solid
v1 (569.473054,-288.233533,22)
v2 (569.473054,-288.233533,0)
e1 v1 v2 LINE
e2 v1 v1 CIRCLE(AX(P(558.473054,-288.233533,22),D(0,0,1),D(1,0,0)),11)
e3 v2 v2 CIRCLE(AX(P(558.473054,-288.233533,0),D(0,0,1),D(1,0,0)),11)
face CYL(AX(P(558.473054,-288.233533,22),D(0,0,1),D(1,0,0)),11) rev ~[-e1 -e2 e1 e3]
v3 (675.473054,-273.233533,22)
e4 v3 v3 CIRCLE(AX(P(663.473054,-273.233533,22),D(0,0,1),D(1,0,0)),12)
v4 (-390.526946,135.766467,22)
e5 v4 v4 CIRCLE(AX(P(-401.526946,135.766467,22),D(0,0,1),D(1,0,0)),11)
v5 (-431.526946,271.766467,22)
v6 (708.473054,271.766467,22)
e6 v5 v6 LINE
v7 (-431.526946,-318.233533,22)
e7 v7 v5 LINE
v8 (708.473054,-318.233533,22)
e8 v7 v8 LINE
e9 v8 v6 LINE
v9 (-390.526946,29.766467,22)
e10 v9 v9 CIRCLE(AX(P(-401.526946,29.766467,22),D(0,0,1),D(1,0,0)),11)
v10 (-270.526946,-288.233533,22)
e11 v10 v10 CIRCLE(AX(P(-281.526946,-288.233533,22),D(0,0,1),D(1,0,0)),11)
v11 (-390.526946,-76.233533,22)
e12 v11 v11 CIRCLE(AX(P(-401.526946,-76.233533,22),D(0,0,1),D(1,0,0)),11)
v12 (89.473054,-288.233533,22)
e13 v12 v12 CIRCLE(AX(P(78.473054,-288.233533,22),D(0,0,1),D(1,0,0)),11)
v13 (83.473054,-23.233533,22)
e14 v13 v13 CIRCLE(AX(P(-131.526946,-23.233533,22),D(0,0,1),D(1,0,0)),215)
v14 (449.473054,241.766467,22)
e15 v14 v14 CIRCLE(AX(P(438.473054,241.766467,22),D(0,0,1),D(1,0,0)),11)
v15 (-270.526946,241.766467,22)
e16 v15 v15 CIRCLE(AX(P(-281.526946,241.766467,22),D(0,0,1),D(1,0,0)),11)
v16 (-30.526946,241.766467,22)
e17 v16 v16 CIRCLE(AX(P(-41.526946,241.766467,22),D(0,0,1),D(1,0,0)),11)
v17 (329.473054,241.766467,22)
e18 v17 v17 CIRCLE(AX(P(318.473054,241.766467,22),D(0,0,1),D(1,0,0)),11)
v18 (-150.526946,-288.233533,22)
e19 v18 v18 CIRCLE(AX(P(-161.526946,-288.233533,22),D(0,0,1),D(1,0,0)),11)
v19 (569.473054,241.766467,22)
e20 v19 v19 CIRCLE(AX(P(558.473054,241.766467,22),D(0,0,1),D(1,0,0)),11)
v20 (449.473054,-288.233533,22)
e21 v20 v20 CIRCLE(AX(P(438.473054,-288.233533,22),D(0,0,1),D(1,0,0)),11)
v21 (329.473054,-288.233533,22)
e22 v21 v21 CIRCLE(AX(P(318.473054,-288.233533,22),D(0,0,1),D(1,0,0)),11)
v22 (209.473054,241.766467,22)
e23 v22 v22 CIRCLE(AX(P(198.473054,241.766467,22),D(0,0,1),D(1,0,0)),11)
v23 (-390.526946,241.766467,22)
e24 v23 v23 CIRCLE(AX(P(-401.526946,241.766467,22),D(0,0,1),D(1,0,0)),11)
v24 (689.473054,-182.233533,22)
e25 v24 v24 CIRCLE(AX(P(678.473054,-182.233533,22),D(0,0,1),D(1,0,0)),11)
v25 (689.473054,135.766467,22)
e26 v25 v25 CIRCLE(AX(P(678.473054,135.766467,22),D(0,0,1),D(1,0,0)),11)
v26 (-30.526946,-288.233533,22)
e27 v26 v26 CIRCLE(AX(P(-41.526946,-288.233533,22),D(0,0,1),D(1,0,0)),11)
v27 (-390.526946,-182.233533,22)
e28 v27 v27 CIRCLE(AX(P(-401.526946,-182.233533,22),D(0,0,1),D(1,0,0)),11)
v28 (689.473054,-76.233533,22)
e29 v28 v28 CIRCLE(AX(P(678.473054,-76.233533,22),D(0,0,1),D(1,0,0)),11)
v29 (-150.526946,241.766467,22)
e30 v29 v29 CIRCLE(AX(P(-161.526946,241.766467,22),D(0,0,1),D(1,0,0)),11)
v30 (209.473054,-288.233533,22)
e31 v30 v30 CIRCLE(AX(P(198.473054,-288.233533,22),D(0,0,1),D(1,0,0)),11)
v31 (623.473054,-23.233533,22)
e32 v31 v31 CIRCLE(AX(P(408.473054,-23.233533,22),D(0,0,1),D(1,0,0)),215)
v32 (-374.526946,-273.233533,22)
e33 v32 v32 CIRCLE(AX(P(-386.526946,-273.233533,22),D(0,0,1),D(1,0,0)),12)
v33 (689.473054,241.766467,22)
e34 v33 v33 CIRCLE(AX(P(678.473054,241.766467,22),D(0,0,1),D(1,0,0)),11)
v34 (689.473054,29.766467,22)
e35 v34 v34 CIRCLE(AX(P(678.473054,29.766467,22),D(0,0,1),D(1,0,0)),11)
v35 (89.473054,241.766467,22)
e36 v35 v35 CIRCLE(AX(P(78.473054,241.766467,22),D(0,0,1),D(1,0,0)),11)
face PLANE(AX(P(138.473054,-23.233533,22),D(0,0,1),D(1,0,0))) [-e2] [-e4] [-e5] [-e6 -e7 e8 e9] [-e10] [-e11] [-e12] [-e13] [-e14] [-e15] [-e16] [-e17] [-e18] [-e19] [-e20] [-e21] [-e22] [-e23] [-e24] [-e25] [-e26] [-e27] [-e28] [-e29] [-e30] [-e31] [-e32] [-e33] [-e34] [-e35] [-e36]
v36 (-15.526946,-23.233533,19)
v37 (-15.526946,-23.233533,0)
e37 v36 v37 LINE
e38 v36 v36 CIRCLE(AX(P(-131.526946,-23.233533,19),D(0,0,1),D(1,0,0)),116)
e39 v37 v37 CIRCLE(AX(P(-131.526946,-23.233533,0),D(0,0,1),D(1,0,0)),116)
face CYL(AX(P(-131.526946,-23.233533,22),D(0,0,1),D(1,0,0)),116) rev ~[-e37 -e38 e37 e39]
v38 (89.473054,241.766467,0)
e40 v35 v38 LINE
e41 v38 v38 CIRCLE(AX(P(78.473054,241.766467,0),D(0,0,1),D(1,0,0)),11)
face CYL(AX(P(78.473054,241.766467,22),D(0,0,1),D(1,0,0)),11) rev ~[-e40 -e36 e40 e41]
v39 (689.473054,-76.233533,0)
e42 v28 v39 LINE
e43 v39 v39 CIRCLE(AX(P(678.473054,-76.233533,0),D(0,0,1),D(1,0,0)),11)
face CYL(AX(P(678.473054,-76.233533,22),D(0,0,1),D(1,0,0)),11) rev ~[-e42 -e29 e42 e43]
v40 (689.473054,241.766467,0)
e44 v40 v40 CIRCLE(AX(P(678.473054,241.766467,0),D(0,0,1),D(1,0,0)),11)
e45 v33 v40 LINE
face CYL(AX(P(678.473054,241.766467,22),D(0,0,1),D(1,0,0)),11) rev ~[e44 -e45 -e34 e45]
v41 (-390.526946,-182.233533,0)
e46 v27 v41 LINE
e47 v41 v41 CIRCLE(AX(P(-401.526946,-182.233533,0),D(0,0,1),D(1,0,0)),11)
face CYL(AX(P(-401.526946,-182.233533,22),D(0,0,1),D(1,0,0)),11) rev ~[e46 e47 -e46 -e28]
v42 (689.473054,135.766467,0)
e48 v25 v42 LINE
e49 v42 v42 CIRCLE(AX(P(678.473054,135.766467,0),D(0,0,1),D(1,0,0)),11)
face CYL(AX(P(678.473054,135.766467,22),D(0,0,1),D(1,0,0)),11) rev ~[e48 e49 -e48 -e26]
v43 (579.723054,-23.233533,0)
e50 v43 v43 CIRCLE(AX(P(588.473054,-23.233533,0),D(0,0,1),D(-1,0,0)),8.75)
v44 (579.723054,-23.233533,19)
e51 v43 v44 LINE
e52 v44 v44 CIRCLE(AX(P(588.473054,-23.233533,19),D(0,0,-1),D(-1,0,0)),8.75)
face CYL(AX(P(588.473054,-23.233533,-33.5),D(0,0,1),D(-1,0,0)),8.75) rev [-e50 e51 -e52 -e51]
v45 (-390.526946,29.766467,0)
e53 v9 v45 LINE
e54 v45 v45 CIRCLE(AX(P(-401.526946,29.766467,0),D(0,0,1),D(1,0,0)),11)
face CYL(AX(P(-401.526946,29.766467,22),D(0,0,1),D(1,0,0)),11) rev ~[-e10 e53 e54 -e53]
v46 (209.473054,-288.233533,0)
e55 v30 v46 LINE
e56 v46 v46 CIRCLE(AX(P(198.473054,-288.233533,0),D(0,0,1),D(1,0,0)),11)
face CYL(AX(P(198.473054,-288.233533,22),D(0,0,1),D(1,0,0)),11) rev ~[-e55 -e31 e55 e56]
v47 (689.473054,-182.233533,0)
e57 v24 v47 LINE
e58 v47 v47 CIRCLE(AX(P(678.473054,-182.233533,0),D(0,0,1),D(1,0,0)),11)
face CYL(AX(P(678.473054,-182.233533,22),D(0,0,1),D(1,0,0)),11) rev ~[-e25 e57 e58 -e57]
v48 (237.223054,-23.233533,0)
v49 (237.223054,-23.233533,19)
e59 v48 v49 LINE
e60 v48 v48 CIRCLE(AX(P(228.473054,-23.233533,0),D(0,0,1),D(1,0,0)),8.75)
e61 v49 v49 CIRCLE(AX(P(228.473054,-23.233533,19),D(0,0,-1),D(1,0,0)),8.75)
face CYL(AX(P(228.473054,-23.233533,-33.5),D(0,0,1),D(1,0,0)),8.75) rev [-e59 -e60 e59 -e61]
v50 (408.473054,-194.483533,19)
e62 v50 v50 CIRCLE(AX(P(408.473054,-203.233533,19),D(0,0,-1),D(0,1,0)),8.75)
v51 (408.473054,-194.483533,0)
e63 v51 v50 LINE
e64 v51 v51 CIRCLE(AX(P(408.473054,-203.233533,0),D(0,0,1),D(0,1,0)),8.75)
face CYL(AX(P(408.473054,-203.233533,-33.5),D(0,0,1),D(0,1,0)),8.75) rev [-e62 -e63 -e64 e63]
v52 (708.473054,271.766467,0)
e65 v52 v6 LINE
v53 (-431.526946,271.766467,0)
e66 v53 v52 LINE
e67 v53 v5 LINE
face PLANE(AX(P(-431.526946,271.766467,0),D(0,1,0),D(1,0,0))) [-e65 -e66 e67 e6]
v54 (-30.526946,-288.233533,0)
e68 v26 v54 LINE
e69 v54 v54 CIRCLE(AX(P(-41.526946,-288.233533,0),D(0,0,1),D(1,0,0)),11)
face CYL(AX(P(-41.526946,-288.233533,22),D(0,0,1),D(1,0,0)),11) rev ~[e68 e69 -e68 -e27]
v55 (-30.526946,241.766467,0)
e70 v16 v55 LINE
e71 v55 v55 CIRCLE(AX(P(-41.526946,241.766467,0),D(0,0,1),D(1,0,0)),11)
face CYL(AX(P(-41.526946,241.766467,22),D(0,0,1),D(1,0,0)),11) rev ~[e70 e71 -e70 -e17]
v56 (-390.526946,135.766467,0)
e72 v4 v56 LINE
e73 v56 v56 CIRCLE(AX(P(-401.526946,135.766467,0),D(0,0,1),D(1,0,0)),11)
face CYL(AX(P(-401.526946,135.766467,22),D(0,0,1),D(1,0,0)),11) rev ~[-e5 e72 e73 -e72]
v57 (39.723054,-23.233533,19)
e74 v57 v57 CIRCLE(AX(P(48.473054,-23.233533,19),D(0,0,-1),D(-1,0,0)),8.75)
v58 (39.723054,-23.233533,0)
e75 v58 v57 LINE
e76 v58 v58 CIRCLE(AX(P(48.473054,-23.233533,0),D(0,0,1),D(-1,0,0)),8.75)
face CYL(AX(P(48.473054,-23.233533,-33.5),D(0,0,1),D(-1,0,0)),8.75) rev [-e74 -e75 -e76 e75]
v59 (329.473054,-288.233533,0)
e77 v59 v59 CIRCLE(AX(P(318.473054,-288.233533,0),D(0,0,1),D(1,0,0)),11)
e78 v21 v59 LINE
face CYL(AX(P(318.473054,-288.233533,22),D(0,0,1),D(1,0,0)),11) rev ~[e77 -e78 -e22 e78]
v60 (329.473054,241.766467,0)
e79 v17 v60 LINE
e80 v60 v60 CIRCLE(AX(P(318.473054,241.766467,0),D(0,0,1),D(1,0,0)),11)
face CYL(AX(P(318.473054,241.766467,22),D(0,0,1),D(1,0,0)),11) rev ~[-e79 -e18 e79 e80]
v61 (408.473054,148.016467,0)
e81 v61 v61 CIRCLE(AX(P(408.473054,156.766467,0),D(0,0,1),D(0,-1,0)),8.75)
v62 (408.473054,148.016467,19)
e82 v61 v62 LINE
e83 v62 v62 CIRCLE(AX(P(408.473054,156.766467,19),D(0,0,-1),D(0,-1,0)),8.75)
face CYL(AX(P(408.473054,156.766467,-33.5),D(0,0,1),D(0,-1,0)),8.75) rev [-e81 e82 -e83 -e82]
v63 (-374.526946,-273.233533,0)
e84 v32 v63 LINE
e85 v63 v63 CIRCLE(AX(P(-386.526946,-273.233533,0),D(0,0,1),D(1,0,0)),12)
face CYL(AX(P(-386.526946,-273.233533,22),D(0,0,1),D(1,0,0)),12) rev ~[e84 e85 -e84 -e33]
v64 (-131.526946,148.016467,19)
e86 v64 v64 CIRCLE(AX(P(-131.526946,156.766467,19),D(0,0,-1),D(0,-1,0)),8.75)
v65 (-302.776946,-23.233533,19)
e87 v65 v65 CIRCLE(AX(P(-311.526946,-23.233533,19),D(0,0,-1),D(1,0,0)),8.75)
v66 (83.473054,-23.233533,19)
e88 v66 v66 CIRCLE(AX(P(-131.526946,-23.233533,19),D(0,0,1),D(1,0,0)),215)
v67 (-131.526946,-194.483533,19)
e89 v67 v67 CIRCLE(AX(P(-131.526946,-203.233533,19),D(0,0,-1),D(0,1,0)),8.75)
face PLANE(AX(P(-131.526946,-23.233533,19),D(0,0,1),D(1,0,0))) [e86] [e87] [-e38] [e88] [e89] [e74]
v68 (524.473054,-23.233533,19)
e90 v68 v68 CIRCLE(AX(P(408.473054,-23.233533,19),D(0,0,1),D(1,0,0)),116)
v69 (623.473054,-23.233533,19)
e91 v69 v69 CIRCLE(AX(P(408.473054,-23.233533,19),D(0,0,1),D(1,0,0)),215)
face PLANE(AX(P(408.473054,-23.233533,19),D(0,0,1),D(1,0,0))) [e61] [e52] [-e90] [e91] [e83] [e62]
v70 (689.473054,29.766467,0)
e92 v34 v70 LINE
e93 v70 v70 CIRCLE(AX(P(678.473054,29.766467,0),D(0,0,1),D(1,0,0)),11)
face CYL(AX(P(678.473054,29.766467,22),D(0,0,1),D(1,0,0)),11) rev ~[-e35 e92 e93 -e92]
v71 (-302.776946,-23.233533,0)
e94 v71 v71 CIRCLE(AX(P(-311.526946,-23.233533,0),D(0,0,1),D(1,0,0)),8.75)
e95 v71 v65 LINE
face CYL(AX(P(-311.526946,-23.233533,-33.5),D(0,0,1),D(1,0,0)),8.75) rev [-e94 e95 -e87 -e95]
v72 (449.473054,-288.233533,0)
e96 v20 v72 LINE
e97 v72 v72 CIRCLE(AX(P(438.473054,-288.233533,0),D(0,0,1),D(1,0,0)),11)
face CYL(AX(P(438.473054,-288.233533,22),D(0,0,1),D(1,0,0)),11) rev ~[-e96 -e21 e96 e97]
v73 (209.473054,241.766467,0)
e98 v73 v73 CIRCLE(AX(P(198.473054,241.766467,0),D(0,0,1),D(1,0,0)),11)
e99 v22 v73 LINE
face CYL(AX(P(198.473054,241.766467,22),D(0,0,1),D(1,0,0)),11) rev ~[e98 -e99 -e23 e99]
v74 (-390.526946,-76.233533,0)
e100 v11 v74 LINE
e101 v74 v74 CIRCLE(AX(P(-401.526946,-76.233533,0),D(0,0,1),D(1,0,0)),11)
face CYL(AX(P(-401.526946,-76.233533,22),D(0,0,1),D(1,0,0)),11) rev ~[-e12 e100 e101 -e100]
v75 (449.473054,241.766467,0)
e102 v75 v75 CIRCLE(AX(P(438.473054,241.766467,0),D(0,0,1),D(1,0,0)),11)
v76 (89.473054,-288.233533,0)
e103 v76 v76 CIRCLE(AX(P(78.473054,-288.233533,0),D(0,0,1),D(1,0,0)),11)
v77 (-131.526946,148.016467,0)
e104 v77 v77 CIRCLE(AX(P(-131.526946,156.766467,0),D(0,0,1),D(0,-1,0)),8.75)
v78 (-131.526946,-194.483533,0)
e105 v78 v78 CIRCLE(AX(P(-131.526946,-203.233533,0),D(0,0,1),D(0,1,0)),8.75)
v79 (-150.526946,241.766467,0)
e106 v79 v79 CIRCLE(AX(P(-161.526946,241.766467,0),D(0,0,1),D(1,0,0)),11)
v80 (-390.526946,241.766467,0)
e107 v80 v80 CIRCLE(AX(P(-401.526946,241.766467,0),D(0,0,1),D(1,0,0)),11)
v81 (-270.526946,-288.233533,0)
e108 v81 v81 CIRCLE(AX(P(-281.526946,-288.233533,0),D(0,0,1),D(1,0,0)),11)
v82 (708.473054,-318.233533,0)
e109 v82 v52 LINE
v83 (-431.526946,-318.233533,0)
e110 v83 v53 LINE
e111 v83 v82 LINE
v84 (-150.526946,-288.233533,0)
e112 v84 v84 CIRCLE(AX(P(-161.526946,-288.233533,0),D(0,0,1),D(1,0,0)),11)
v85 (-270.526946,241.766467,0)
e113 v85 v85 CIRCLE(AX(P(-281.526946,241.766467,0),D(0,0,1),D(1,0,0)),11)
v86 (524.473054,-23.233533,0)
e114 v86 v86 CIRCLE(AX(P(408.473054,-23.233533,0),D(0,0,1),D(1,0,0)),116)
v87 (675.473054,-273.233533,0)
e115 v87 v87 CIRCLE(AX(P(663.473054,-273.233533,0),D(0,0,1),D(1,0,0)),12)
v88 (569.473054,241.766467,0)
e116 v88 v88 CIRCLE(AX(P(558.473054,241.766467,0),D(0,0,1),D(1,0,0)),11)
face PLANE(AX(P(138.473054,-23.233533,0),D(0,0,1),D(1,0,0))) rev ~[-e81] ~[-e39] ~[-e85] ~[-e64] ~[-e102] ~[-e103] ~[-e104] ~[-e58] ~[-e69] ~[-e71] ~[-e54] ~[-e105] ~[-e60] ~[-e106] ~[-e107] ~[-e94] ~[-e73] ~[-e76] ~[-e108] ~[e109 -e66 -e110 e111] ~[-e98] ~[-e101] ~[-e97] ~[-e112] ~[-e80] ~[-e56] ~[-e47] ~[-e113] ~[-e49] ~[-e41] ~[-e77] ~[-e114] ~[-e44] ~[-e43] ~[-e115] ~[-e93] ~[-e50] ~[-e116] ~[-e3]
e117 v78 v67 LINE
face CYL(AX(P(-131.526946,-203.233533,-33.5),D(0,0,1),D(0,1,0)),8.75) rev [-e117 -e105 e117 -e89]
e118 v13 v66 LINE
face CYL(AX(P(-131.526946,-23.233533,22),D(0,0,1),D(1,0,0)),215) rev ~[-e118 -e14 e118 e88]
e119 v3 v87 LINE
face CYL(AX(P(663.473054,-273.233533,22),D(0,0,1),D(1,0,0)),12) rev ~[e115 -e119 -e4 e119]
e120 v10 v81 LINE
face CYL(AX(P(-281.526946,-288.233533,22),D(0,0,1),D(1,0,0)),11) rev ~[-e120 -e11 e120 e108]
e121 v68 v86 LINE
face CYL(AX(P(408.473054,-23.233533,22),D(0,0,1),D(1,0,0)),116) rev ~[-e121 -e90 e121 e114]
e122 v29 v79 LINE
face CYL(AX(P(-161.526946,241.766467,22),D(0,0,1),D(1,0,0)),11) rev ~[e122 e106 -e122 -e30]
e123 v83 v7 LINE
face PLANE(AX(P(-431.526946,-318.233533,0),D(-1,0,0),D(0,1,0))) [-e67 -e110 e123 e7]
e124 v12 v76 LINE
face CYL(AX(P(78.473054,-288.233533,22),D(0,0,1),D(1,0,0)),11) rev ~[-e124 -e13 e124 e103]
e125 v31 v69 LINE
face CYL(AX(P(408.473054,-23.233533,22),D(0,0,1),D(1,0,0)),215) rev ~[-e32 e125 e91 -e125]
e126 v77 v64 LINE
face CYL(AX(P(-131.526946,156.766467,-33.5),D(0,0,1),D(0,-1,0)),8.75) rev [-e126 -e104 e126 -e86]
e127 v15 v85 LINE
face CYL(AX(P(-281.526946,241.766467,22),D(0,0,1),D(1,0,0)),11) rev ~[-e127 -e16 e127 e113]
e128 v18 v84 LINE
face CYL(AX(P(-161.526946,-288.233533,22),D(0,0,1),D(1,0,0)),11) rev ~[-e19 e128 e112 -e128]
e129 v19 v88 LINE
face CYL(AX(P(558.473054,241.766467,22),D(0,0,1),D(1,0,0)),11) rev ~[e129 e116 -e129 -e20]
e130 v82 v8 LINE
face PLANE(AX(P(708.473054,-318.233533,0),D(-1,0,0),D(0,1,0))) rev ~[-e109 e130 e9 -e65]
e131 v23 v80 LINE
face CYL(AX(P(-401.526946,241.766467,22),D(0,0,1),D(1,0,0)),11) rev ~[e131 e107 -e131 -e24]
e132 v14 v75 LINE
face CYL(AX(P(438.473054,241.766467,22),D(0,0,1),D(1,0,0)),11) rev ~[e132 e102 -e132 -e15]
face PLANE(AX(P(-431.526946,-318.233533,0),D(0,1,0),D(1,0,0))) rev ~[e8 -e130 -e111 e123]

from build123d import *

# Parameters (mm, degrees)
SKETCH1_W           = 1140
SKETCH1_H           = 590
BOSS_EXTRUDE1_DEPTH = 22
SKETCH2_R           = 11
SKETCH2_R_2         = 12
CUT_EXTRUDE1_DEPTH  = 32
SKETCH3_R           = 116
CUT_EXTRUDE2_DEPTH  = 32
SKETCH4_R           = 215
CUT_EXTRUDE3_DEPTH  = 3
CIRPATTERN1_COUNT   = 4
CIRCPATTERN2_COUNT  = 4


with BuildPart() as part:
    # Sketch1 → Boss-Extrude1 (new body)
    with BuildSketch(Plane.XY):
        with Locations((138.473053892, -23.233532934)):
            Rectangle(SKETCH1_W, SKETCH1_H)
    extrude(amount=BOSS_EXTRUDE1_DEPTH)

    # Sketch2 → Cut-Extrude1 (cut)
    with BuildSketch(Plane.XY.offset(22)):
        with Locations((-401.526946108, 241.766467066)):
            Circle(SKETCH2_R)
        with Locations((-281.526946108, 241.766467066)):
            Circle(SKETCH2_R)
        with Locations((-161.526946108, 241.766467066)):
            Circle(SKETCH2_R)
        with Locations((-41.526946108, 241.766467066)):
            Circle(SKETCH2_R)
        with Locations((78.473053892, 241.766467066)):
            Circle(SKETCH2_R)
        with Locations((198.473053892, 241.766467066)):
            Circle(SKETCH2_R)
        with Locations((318.473053892, 241.766467066)):
            Circle(SKETCH2_R)
        with Locations((438.473053892, 241.766467066)):
            Circle(SKETCH2_R)
        with Locations((558.473053892, 241.766467066)):
            Circle(SKETCH2_R)
        with Locations((678.473053892, 241.766467066)):
            Circle(SKETCH2_R)
        with Locations((-386.526946108, -273.233532934)):
            Circle(SKETCH2_R_2)
        with Locations((558.473053892, -288.233532934)):
            Circle(SKETCH2_R)
        with Locations((438.473053892, -288.233532934)):
            Circle(SKETCH2_R)
        with Locations((318.473053892, -288.233532934)):
            Circle(SKETCH2_R)
        with Locations((198.473053892, -288.233532934)):
            Circle(SKETCH2_R)
        with Locations((78.473053892, -288.233532934)):
            Circle(SKETCH2_R)
        with Locations((-41.526946108, -288.233532934)):
            Circle(SKETCH2_R)
        with Locations((-161.526946108, -288.233532934)):
            Circle(SKETCH2_R)
        with Locations((-281.526946108, -288.233532934)):
            Circle(SKETCH2_R)
        with Locations((663.473053892, -273.233532934)):
            Circle(SKETCH2_R_2)
        with Locations((-401.526946108, 135.766467066)):
            Circle(SKETCH2_R)
        with Locations((-401.526946108, 29.766467066)):
            Circle(SKETCH2_R)
        with Locations((-401.526946108, -76.233532934)):
            Circle(SKETCH2_R)
        with Locations((-401.526946108, -182.233532934)):
            Circle(SKETCH2_R)
        with Locations((678.473053892, -182.233532934)):
            Circle(SKETCH2_R)
        with Locations((678.473053892, -76.233532934)):
            Circle(SKETCH2_R)
        with Locations((678.473053892, 29.766467066)):
            Circle(SKETCH2_R)
        with Locations((678.473053892, 135.766467066)):
            Circle(SKETCH2_R)
    extrude(amount=-CUT_EXTRUDE1_DEPTH, mode=Mode.SUBTRACT)

    # Sketch3 → Cut-Extrude2 (cut)
    with BuildSketch(Plane.XY.offset(22)):
        with Locations((-131.526946108, -23.233532934)):
            Circle(SKETCH3_R)
        with Locations((408.473053892, -23.233532934)):
            Circle(SKETCH3_R)
    extrude(amount=-CUT_EXTRUDE2_DEPTH, mode=Mode.SUBTRACT)

    # Sketch4 → Cut-Extrude3 (cut)
    with BuildSketch(Plane.XY.offset(22)):
        with Locations((-131.526946108, -23.233532934)):
            Circle(SKETCH4_R)
        with Locations((408.473053892, -23.233532934)):
            Circle(SKETCH4_R)
    extrude(amount=-CUT_EXTRUDE3_DEPTH, mode=Mode.SUBTRACT)

    # Sketch6 → M20 Tapped Hole1 (revolve, cut)
    with BuildSketch(Plane(origin=(-131.526946108, 156.766467066, 19), x_dir=(0, -1, 0), z_dir=(1, 0, 0))):
        Polygon((0, 0), (0, 57.757530416), (8.75, 52.5), (8.75, 0), align=None)
    m20_tapped_hole1 = revolve(axis=Axis((-131.526946108, 156.766467066, 25.35), (0, 0, -1)), mode=Mode.SUBTRACT)

    # CirPattern1: M20 Tapped Hole1 ×4 about axis
    cirpattern1_axis = Axis((-131.526946108, -23.233532934, 0), (0, 0, 1))
    for i in range(1, CIRPATTERN1_COUNT):
        add(m20_tapped_hole1.rotate(cirpattern1_axis, i * 360 / CIRPATTERN1_COUNT), mode=Mode.SUBTRACT)

    # Sketch8 → M20 Tapped Hole2 (revolve, cut)
    with BuildSketch(Plane(origin=(408.473053892, 156.766467066, 19), x_dir=(0, -1, 0), z_dir=(1, 0, 0))):
        Polygon((0, 0), (0, 57.757530416), (8.75, 52.5), (8.75, 0), align=None)
    m20_tapped_hole2 = revolve(axis=Axis((408.473053892, 156.766467066, 25.35), (0, 0, -1)), mode=Mode.SUBTRACT)

    # CircPattern2: M20 Tapped Hole2 ×4 about axis
    circpattern2_axis = Axis((408.473053892, -23.233532934, 0), (0, 0, 1))
    for i in range(1, CIRCPATTERN2_COUNT):
        add(m20_tapped_hole2.rotate(circpattern2_axis, i * 360 / CIRCPATTERN2_COUNT), mode=Mode.SUBTRACT)


solid = part.part
